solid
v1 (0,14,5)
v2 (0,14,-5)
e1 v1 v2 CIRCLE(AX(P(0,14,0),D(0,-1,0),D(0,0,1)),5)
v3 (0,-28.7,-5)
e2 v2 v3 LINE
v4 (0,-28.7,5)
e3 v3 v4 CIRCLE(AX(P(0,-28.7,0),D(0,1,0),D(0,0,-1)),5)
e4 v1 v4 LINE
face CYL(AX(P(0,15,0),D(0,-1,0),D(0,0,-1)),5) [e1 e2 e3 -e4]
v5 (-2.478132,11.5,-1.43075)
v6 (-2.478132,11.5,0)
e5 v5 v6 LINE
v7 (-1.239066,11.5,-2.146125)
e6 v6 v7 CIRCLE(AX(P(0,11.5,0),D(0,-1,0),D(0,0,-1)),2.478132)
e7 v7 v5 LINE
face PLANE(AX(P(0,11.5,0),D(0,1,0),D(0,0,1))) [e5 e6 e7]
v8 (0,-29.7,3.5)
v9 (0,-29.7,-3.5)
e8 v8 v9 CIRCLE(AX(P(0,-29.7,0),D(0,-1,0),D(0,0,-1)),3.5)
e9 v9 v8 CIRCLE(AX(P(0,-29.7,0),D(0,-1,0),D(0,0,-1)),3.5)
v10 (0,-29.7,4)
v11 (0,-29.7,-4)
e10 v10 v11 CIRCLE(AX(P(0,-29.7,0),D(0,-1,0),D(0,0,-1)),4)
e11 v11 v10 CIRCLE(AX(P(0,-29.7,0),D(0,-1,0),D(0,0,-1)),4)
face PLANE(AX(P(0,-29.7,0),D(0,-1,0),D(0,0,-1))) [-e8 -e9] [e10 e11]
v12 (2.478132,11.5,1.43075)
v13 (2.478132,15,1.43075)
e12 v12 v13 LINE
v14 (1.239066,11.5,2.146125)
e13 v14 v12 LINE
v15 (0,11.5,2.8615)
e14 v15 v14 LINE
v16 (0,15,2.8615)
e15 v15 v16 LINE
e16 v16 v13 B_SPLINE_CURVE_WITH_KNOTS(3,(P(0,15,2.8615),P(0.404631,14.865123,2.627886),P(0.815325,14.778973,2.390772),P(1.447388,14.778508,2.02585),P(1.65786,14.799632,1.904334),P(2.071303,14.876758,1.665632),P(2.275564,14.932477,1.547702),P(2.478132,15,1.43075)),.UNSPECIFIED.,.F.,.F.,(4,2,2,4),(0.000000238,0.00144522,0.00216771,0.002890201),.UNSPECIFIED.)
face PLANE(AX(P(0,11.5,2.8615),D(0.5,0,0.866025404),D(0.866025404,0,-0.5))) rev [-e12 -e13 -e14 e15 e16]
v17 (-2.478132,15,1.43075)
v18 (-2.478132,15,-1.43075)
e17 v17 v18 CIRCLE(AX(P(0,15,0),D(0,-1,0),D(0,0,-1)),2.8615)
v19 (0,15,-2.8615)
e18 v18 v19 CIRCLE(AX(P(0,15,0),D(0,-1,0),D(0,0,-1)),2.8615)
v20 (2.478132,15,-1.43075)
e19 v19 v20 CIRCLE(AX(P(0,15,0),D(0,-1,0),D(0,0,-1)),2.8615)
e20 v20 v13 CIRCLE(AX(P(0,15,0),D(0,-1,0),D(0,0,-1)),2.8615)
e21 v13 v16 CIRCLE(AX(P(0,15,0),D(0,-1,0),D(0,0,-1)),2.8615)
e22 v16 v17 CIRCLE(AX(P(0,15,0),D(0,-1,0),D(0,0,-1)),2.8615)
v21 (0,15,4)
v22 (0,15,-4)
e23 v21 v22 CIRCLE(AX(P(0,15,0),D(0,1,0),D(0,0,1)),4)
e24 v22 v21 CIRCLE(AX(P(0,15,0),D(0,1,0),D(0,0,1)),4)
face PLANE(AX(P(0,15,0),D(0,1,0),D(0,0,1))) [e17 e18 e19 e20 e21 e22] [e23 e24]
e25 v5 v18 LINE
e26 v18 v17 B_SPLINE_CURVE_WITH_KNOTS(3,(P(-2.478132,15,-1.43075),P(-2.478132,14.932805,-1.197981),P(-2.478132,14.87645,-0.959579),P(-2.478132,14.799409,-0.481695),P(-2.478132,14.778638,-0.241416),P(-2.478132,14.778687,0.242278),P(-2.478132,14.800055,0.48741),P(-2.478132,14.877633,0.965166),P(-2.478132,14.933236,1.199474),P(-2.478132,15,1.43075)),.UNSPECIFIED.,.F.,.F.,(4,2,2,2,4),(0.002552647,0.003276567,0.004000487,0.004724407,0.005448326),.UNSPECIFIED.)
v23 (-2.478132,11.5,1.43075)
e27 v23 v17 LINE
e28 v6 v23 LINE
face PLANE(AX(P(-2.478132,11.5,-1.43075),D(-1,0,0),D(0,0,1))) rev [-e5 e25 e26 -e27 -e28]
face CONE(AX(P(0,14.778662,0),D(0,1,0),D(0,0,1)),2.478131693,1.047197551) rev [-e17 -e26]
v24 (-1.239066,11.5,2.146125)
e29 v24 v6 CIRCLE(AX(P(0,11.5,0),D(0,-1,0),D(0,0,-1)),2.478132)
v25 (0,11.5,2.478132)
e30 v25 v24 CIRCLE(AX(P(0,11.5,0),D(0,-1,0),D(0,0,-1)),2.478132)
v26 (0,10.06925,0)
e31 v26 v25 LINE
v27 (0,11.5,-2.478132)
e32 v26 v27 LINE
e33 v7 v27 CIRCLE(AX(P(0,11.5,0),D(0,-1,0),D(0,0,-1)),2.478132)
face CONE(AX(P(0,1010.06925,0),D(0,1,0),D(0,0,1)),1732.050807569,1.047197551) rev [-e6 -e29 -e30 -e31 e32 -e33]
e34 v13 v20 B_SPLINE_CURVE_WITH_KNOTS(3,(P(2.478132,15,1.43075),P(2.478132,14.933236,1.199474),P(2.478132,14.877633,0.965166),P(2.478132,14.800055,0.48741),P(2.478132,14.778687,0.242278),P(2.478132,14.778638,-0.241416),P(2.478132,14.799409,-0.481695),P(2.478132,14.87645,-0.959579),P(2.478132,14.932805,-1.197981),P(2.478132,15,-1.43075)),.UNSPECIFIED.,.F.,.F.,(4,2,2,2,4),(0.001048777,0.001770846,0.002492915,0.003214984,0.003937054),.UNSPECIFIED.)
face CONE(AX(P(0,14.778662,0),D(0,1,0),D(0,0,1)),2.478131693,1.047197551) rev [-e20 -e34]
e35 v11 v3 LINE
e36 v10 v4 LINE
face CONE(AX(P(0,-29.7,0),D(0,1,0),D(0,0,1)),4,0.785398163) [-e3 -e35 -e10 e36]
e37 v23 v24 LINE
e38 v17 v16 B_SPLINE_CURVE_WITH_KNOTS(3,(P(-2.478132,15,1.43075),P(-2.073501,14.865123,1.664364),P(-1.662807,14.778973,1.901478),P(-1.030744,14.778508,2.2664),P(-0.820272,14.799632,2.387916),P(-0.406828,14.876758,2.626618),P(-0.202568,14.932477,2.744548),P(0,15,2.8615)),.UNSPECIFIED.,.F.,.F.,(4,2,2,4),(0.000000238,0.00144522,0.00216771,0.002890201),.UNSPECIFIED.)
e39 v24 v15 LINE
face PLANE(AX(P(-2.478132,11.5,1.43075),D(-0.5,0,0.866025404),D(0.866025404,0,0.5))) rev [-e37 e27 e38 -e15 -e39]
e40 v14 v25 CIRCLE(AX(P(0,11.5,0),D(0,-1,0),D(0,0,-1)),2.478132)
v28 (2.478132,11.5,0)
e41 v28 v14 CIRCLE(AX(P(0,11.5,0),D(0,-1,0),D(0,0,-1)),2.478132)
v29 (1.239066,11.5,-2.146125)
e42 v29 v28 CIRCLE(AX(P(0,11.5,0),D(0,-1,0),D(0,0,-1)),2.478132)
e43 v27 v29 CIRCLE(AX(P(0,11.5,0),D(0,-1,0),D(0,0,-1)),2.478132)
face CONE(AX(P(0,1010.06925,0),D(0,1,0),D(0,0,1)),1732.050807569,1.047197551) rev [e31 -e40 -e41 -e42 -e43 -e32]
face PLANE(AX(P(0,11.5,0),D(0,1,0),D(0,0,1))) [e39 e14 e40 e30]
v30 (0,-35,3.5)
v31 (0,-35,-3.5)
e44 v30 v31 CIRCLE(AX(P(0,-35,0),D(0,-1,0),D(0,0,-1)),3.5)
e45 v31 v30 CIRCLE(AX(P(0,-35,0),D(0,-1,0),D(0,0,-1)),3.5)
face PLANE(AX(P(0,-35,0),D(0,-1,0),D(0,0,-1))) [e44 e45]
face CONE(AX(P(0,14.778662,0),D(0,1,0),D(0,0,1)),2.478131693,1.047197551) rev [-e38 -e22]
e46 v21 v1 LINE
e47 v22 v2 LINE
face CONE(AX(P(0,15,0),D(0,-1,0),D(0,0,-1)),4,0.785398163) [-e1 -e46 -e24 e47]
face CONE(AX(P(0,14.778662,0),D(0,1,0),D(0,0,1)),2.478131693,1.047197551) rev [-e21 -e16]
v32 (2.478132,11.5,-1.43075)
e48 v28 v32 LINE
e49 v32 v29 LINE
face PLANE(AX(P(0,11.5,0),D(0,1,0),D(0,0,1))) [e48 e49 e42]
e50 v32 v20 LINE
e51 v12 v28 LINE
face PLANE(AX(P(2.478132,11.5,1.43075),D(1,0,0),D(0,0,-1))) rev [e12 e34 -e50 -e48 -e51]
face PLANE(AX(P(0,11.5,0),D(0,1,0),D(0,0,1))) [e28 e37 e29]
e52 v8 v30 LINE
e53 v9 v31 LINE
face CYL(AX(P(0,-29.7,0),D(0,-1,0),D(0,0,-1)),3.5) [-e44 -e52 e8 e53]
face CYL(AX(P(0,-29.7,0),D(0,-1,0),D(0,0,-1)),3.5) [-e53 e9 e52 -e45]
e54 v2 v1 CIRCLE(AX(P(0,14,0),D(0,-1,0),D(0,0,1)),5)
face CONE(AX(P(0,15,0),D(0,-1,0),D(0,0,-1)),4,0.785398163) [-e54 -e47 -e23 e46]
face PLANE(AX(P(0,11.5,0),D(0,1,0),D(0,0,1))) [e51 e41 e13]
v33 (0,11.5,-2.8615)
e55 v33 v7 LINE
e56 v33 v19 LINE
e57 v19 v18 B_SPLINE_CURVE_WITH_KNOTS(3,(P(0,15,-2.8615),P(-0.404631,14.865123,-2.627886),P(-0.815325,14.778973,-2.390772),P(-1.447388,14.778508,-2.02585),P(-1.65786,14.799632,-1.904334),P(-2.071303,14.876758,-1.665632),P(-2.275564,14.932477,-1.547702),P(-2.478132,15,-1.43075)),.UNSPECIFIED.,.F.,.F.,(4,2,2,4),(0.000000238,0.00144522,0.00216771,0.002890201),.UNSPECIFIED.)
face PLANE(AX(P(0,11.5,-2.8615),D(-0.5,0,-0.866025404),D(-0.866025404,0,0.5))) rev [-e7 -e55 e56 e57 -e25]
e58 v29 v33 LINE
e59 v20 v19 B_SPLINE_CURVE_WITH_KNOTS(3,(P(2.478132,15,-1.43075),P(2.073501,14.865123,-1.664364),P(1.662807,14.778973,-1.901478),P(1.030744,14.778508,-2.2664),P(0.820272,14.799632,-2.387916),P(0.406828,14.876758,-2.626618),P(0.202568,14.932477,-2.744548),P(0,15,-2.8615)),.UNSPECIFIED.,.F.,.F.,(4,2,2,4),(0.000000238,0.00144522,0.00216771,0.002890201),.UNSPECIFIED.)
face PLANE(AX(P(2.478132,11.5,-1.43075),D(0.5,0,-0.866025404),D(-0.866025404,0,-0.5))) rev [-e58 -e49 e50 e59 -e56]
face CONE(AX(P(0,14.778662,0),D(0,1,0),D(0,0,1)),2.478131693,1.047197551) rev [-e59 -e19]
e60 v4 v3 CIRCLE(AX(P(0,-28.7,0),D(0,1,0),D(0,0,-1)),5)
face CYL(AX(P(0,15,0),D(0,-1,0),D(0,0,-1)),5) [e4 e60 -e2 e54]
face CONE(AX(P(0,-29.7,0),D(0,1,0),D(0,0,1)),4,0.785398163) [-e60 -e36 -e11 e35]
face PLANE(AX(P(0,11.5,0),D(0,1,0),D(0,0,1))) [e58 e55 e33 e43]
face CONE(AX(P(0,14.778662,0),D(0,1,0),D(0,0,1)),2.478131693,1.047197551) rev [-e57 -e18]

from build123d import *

# Parameters (mm, degrees)
SKETCH1_R           = 5
BOSS_EXTRUDE1_DEPTH = 15
BOSS_EXTRUDE2_START = 35
SKETCH2_R           = 5
BOSS_EXTRUDE2_DEPTH = 35
CUT_EXTRUDE1_DEPTH  = 3.5
SKETCH5_R           = 5
SKETCH5_R_2         = 3.5
CUT_EXTRUDE2_DEPTH  = 5.3
CHAMFER1_SIZE       = 1


with BuildPart() as part:
    # Sketch1 → Boss-Extrude1 (new body)
    with BuildSketch(Plane(origin=(0, 0, 0), x_dir=(1, 0, 0), z_dir=(0, 1, 0))):
        with Locations(Location((0, 0, 0), (0, 0, 270))):
            Circle(SKETCH1_R)
    extrude(amount=BOSS_EXTRUDE1_DEPTH)

    # Sketch2 → Boss-Extrude2 (add)
    with BuildSketch(Plane.XZ.offset(BOSS_EXTRUDE2_START)):
        with Locations(Location((0, 0, 0), (0, 0, 270))):
            Circle(SKETCH2_R)
    extrude(amount=-BOSS_EXTRUDE2_DEPTH)

    # Sketch3 → Cut-Extrude1 (cut)
    with BuildSketch(Plane(origin=(0, 15, 0), x_dir=(1, 0, 0), z_dir=(0, 1, 0))):
        Polygon((0, 2.8615), (-2.478131693, 1.43075), (-2.478131693, -1.43075), (0, -2.8615), (2.478131693, -1.43075), (2.478131693, 1.43075), align=None)
    extrude(amount=-CUT_EXTRUDE1_DEPTH, mode=Mode.SUBTRACT)

    # Sketch4 → Cut-Revolve1 (revolve, cut)
    with BuildSketch(Plane.XY, mode=Mode.PRIVATE) as cut_revolve1_sk:
        Polygon((0, 11.5), (2.478131693, 11.5), (0, 10.06925), align=None)
        Polygon((2.478131693, 14.778662205), (2.478131693, 15), (2.8615, 15), align=None)
    revolve(cut_revolve1_sk.sketch.rotate(Axis((0, -3.932195077, 0), (0, 1, 0)), 90), axis=Axis((0, -3.932195077, 0), (0, 1, 0)), mode=Mode.SUBTRACT)

    # Sketch5 → Cut-Extrude2 (cut)
    with BuildSketch(Plane.XZ.offset(35)):
        with Locations(Location((0, 0, 0), (0, 0, 270))):
            Circle(SKETCH5_R)
        with Locations(Location((0, 0, 0), (0, 0, 270))):
            Circle(SKETCH5_R_2, mode=Mode.SUBTRACT)
    extrude(amount=-CUT_EXTRUDE2_DEPTH, mode=Mode.SUBTRACT)

    # Chamfer1
    chamfer1_edges = [part.edges().sort_by_distance(p)[0] for p in [
        (0, 15, -5),
        (0, -29.7, 5),
    ]]
    chamfer(chamfer1_edges, length=CHAMFER1_SIZE)


solid = part.part
